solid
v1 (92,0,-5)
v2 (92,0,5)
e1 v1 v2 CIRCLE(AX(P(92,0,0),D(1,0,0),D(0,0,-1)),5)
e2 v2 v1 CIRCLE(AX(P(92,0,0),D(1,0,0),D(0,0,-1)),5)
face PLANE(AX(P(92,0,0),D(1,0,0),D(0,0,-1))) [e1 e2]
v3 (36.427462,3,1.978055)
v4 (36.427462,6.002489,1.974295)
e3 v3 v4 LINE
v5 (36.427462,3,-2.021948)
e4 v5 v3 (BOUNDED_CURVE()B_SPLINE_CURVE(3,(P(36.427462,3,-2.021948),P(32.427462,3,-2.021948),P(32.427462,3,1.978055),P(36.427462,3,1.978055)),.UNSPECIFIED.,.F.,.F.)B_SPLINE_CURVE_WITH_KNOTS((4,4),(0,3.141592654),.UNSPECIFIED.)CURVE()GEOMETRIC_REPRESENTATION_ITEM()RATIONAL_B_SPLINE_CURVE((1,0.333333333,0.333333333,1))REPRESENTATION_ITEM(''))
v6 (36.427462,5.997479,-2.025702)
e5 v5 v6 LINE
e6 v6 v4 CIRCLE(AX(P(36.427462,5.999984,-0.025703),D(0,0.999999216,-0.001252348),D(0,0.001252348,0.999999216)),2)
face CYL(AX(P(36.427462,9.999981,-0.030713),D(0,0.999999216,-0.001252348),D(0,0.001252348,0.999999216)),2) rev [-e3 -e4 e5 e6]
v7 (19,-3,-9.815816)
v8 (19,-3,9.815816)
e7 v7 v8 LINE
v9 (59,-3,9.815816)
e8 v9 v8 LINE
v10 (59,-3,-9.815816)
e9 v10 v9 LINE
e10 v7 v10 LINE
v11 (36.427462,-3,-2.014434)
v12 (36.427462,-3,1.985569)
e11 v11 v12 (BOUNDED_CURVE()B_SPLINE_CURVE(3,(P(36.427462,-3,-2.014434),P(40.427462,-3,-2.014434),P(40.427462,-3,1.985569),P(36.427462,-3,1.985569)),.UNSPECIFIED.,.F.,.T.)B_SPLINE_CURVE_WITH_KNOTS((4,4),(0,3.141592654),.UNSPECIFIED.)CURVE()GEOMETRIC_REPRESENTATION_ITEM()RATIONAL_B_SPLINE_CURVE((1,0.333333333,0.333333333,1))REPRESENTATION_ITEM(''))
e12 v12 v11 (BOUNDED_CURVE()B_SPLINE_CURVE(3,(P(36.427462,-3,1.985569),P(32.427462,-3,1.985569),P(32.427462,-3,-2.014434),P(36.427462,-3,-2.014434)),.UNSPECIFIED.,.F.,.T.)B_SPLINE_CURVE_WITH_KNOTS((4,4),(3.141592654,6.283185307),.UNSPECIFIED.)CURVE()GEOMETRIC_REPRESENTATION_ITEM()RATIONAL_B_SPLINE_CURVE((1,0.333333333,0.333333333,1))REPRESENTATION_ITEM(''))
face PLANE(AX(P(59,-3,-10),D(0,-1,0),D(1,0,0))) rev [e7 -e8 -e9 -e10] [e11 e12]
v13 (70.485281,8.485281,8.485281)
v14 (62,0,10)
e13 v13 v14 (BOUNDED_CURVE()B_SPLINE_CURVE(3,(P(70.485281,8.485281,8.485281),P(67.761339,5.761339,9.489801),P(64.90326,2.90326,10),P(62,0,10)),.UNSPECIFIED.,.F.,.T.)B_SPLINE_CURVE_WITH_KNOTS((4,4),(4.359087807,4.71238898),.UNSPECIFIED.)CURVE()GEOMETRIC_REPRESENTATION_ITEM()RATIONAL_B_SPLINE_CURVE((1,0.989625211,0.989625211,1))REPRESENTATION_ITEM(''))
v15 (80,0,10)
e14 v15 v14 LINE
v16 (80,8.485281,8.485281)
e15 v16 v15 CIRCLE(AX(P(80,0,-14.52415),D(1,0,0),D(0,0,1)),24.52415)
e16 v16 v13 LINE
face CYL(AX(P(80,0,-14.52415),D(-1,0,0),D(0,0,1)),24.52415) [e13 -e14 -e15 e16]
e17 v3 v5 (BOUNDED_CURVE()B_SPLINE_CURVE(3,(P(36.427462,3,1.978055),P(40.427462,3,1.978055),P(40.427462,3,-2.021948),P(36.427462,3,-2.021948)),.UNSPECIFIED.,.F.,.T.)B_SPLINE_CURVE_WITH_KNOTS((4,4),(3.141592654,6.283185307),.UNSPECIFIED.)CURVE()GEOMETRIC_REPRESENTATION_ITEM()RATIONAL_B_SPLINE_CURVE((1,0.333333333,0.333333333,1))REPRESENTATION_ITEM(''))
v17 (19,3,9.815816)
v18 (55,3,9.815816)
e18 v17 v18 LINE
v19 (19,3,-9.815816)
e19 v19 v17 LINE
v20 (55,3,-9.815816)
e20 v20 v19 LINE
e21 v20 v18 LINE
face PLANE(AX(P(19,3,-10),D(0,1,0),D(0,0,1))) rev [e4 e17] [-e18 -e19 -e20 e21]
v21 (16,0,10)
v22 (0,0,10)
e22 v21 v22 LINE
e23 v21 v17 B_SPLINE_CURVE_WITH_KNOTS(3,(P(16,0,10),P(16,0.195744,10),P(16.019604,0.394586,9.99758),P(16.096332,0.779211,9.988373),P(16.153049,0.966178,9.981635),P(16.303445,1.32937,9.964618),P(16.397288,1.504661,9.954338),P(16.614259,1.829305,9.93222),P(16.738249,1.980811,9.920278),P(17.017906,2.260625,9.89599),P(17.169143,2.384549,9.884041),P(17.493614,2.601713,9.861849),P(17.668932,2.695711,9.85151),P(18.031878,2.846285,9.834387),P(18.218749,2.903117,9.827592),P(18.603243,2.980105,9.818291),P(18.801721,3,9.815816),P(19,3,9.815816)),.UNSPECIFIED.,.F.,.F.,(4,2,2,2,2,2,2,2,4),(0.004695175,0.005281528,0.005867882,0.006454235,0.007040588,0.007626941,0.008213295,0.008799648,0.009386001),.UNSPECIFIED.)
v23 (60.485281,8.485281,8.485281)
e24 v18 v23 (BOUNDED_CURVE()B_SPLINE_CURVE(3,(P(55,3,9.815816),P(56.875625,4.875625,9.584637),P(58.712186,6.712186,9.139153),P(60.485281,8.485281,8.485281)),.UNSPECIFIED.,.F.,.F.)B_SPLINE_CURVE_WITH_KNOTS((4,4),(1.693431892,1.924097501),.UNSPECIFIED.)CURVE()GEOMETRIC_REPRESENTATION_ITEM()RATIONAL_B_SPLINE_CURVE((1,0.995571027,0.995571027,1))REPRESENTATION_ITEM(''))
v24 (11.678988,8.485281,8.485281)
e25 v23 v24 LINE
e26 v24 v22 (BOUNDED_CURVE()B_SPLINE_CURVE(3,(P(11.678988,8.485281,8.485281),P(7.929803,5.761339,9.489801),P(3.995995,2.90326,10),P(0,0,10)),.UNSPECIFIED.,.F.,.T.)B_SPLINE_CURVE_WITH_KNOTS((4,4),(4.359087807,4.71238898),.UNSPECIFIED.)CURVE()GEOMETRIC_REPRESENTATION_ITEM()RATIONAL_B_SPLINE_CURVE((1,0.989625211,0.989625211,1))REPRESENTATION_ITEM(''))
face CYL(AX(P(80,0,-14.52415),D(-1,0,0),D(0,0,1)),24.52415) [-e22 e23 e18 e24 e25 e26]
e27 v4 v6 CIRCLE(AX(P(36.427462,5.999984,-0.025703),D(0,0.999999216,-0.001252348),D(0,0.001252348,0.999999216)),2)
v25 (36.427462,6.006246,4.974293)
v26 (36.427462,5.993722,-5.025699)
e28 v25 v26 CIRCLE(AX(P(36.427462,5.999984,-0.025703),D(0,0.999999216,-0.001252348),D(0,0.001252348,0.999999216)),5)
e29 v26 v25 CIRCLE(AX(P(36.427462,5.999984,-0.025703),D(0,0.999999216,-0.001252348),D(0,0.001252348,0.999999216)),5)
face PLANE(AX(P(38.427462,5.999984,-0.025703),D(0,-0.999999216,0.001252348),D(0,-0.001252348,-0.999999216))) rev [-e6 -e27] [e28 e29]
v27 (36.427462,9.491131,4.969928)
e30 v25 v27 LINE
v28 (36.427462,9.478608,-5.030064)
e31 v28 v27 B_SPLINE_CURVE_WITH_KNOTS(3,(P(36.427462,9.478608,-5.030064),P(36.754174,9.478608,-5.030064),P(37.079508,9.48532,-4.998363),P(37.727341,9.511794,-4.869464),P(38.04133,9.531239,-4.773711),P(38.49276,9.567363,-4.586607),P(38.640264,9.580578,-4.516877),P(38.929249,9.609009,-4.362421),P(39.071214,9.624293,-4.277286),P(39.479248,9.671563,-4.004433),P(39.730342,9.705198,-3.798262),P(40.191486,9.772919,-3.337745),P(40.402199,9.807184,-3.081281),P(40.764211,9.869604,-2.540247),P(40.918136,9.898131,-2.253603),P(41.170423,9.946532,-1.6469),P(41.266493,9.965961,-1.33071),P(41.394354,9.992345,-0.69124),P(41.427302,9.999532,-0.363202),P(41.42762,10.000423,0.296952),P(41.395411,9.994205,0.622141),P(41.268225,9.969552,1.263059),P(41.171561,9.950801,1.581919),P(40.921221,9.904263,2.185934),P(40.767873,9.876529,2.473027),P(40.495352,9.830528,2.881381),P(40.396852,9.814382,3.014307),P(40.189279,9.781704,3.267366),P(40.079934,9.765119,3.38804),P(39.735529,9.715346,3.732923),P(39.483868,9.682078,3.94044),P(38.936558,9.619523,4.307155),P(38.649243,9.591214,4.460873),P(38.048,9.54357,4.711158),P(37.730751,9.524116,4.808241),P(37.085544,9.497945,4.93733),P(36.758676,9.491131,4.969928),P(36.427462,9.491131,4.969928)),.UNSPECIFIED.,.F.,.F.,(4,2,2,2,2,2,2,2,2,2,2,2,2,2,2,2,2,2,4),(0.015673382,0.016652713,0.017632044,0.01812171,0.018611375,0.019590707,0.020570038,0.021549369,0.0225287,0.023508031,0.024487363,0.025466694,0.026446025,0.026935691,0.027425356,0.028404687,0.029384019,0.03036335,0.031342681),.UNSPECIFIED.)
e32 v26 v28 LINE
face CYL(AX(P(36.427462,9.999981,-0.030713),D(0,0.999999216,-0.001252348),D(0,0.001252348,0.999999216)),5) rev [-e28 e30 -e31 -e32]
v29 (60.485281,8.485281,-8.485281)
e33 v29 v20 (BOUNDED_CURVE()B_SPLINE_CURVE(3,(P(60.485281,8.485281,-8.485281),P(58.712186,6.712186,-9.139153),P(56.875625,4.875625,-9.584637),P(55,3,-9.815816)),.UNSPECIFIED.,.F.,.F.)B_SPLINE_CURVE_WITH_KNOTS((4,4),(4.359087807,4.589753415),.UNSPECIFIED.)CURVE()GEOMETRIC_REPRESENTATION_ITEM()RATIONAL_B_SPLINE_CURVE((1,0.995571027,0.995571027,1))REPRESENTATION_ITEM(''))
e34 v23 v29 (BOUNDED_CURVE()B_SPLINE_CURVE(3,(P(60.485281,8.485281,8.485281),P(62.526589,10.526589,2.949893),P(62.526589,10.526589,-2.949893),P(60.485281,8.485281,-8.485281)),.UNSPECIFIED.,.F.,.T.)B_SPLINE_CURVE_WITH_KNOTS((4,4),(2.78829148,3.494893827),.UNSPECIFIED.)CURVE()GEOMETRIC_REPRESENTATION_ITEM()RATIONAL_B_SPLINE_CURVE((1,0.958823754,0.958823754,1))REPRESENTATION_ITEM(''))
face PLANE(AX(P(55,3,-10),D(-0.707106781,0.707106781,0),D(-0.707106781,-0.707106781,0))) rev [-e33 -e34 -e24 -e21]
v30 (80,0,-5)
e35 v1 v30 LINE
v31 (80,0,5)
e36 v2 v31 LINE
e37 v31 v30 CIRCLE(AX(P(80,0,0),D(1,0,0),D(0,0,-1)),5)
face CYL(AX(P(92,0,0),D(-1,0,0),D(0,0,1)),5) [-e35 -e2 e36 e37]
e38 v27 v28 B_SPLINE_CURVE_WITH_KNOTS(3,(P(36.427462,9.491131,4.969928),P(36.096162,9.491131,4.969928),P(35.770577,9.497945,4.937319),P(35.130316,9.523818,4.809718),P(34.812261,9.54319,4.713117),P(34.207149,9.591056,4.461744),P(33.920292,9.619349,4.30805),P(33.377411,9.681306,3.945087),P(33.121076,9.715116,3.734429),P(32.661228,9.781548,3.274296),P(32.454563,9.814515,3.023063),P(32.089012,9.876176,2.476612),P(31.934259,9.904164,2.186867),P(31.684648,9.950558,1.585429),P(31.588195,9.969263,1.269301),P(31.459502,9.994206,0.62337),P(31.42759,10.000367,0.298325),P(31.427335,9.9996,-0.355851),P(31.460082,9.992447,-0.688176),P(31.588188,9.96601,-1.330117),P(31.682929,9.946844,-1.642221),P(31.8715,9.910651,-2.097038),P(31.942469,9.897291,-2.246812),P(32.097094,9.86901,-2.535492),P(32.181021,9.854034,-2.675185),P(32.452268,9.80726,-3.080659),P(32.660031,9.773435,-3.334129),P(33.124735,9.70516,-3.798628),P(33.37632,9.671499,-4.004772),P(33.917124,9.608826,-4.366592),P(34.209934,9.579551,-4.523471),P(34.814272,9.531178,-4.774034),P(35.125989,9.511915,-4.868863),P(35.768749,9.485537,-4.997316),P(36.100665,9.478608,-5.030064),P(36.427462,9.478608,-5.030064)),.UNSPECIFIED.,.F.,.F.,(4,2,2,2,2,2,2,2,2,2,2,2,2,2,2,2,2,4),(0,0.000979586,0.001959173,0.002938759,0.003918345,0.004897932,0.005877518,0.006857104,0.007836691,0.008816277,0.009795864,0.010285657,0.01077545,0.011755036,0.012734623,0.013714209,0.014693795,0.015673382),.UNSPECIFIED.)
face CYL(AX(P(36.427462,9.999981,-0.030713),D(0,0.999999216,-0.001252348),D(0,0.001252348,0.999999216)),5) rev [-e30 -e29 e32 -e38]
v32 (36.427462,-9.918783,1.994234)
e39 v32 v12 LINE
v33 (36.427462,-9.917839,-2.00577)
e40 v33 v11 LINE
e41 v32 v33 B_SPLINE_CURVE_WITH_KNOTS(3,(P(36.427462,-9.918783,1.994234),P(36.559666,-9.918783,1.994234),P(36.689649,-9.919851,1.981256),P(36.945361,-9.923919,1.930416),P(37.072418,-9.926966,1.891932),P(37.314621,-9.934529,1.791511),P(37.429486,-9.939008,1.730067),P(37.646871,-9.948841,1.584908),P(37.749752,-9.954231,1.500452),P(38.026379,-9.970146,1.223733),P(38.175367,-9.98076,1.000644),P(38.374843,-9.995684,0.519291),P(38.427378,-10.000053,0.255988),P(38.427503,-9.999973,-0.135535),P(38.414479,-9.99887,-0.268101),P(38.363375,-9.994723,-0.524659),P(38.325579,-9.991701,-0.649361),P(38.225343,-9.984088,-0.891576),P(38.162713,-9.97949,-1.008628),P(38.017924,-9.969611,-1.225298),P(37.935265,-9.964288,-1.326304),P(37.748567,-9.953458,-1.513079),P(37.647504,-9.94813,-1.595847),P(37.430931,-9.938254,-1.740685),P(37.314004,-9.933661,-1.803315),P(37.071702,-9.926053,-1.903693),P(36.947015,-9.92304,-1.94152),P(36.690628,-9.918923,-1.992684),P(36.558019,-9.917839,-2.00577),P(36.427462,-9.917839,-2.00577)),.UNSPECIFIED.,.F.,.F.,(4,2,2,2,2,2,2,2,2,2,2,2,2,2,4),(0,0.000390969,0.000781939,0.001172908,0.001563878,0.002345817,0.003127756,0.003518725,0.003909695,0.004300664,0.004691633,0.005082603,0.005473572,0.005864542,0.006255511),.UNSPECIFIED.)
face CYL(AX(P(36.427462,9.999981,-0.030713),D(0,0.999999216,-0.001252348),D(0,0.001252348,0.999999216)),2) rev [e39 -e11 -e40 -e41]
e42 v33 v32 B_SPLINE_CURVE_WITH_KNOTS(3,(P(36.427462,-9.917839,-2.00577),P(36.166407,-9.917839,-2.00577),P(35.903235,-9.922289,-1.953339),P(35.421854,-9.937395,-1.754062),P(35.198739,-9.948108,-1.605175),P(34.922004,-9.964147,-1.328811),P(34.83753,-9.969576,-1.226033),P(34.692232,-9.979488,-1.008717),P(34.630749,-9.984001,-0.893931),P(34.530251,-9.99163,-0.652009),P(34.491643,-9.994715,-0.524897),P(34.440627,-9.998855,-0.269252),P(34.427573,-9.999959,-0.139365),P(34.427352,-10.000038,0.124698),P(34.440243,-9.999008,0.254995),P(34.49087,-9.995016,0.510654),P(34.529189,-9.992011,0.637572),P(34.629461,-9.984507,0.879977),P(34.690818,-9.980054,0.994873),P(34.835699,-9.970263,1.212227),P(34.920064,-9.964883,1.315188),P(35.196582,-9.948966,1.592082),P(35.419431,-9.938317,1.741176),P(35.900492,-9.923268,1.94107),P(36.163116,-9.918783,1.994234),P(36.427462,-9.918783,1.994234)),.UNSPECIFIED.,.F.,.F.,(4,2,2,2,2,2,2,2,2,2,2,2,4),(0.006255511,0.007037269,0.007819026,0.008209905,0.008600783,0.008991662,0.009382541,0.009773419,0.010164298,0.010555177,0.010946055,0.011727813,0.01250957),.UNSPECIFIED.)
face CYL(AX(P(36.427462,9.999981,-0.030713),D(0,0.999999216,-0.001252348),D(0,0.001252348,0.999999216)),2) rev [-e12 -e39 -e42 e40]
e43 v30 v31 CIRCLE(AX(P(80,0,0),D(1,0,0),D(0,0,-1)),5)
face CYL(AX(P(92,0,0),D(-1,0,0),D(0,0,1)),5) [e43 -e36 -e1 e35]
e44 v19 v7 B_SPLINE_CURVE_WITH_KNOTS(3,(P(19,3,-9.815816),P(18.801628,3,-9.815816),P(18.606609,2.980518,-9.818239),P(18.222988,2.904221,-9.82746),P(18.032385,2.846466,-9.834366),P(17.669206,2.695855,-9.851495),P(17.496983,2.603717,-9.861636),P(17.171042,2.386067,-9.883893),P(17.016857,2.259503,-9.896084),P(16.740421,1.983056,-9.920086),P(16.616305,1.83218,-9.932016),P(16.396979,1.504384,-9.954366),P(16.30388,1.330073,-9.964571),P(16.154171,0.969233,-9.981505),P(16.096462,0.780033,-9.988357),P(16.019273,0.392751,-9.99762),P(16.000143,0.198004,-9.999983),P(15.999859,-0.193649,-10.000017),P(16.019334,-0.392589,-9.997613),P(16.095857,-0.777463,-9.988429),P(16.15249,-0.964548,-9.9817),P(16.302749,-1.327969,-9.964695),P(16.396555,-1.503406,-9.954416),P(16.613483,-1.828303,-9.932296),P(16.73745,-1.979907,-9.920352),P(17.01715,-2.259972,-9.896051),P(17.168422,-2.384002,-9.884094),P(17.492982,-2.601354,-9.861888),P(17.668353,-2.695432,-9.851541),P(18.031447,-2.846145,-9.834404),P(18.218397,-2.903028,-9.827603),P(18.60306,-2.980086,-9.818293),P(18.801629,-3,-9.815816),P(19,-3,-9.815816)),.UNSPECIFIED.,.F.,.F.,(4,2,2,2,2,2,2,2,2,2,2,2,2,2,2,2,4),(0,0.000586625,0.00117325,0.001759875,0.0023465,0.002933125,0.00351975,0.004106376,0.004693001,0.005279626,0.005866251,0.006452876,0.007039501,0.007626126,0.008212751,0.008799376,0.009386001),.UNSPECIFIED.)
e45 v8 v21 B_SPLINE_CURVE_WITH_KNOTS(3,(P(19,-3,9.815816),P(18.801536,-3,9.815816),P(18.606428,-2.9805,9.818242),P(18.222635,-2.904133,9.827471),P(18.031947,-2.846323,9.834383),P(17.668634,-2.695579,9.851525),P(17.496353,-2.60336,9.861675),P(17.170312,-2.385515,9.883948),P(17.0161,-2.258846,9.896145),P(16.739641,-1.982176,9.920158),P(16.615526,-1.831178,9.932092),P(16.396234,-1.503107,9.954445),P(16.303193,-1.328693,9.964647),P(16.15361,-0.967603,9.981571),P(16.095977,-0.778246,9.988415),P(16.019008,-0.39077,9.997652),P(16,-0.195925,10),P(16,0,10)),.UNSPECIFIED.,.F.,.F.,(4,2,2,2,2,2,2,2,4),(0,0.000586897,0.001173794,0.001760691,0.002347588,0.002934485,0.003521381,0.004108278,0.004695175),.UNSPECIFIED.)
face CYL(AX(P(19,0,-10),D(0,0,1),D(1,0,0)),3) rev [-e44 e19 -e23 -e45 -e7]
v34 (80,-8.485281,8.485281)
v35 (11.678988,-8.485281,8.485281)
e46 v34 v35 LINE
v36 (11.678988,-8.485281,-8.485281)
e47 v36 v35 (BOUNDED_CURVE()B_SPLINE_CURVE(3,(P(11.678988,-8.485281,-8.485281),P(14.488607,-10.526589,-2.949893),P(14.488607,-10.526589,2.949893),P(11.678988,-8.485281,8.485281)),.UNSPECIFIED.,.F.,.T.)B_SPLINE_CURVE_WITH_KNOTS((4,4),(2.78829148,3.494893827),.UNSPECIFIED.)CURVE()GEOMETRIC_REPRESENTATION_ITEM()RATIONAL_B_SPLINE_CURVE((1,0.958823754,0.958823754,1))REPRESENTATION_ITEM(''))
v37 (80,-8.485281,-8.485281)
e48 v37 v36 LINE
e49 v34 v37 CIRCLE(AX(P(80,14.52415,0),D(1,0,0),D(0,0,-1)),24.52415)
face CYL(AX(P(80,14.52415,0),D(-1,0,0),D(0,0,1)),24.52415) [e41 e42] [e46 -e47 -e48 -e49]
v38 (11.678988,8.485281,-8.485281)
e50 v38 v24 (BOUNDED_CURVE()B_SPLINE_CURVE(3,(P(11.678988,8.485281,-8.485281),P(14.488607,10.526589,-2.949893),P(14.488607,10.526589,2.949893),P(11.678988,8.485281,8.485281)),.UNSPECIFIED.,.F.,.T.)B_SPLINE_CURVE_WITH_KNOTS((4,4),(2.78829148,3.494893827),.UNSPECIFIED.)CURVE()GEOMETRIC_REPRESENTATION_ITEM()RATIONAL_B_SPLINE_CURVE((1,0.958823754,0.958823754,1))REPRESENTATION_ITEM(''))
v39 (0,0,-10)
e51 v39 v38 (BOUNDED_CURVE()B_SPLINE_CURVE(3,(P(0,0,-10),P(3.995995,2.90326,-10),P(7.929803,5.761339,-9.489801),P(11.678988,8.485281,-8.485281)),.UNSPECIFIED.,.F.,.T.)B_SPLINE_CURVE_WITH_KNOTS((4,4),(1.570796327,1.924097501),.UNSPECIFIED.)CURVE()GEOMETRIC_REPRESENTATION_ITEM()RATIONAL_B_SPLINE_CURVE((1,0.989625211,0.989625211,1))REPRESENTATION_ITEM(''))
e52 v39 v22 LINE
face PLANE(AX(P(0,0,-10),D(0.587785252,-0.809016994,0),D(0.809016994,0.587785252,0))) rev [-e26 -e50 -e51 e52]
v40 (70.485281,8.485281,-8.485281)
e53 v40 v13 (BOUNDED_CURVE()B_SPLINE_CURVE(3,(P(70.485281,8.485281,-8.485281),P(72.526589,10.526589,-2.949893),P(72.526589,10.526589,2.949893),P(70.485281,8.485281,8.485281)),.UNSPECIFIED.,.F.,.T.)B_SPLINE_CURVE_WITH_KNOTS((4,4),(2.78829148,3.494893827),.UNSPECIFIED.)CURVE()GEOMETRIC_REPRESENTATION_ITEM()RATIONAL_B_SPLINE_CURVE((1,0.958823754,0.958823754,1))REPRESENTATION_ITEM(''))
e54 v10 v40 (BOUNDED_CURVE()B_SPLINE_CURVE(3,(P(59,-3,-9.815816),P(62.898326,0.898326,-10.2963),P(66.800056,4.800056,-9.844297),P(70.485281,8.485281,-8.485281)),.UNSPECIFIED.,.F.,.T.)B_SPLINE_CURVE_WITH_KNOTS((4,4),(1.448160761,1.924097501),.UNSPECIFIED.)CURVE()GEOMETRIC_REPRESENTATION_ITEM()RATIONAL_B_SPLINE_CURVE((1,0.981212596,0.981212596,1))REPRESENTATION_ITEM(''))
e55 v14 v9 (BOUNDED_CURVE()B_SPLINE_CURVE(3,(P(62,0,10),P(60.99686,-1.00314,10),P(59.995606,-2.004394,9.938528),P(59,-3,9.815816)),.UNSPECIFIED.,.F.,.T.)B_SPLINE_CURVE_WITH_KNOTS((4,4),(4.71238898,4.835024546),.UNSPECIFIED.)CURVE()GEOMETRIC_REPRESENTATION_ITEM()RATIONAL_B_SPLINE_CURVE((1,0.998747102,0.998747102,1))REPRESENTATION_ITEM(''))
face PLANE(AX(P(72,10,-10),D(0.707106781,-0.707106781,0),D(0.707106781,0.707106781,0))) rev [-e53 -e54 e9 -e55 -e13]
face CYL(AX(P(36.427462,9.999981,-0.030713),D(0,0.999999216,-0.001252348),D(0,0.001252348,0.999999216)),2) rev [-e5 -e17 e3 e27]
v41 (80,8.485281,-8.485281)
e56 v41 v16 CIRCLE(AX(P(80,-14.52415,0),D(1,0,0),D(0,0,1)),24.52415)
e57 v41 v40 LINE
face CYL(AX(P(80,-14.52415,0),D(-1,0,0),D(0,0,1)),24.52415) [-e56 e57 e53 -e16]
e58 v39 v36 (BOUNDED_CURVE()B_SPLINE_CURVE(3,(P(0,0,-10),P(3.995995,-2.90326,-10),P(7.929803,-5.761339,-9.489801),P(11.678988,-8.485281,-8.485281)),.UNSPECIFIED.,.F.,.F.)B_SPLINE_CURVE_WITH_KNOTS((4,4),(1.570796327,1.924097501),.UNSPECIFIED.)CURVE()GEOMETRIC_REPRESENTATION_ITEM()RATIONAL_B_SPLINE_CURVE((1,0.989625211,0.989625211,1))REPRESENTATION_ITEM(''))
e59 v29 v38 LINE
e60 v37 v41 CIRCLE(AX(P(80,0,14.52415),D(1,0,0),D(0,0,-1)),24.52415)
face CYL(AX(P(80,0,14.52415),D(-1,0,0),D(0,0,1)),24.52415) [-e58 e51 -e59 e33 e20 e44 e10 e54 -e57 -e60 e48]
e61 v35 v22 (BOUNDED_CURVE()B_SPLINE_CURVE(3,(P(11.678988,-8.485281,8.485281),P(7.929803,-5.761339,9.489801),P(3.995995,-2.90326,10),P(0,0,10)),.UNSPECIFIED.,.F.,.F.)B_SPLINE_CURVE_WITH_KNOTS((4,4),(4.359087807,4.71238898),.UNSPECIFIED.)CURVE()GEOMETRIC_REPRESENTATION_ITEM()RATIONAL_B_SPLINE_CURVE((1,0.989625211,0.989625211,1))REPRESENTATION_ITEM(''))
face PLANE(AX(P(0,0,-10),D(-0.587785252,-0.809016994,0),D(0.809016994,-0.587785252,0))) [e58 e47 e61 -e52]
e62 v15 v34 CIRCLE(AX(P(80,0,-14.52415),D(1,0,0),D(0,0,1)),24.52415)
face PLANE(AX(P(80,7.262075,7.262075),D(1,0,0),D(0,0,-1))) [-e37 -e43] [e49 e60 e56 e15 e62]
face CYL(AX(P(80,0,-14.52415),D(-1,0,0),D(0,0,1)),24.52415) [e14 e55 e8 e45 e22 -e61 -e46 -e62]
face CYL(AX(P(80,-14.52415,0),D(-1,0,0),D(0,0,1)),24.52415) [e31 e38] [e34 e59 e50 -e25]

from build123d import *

# Parameters (mm, degrees)
PIN_BODY_80MM_DEPTH             = 80
ARROW_NOSE_CUT_DEPTH            = 82.240384046
ARROW_NOSE_CUT_DEPTH_BACK       = 82.240384046
SLOT_AND_STEP_CUT_DEPTH         = 82.240384046
SLOT_AND_STEP_CUT_DEPTH_BACK    = 82.240384046
SPIGOT_PROFILE_10_R             = 5
SPIGOT_10X12_DEPTH              = 12
COUNTERBORED_HOLE_4_D           = 4
COUNTERBORED_HOLE_4_DEPTH       = 100
COUNTERBORED_HOLE_4_CBORE_D     = 10
COUNTERBORED_HOLE_4_CBORE_DEPTH = 4


with BuildPart() as part:
    # Pin Body Profile → Pin Body 80mm (new body)
    with BuildSketch(Plane(origin=(0, 0, 0), x_dir=(0, 0, -1), z_dir=(1, 0, 0))):
        with BuildLine():
            ThreePointArc((-8.485281374, -8.485281374), (-10, 0), (-8.485281374, 8.485281374))
            ThreePointArc((-8.485281374, 8.485281374), (0, 10), (8.485281374, 8.485281374))
            ThreePointArc((8.485281374, 8.485281374), (10, 0), (8.485281374, -8.485281374))
            ThreePointArc((8.485281374, -8.485281374), (0, -10), (-8.485281374, -8.485281374))
        make_face()
    extrude(amount=PIN_BODY_80MM_DEPTH)

    # Arrow Nose Profile 72deg → Arrow Nose Cut (cut, two sides: drawn at the far end of the back side and taken through both)
    with BuildSketch(Plane.XY.offset(-ARROW_NOSE_CUT_DEPTH_BACK)):
        Polygon((0, 10), (0, 0), (13.763819205, 10), align=None)
        Polygon((13.763819205, -10), (0, 0), (0, -10), align=None)
    extrude(amount=ARROW_NOSE_CUT_DEPTH + ARROW_NOSE_CUT_DEPTH_BACK, mode=Mode.SUBTRACT)

    # Slot and Step Profile → Slot and Step Cut (cut, two sides: drawn at the far end of the back side and taken through both)
    with BuildSketch(Plane.XY.offset(-SLOT_AND_STEP_CUT_DEPTH_BACK)):
        with BuildLine():
            Line((72, 10), (59, -3))
            Line((59, -3), (19, -3))
            ThreePointArc((19, -3), (16, 0), (19, 3))
            Line((19, 3), (55, 3))
            Line((55, 3), (62, 10))
            Line((62, 10), (72, 10))
        make_face()
    extrude(amount=SLOT_AND_STEP_CUT_DEPTH + SLOT_AND_STEP_CUT_DEPTH_BACK, mode=Mode.SUBTRACT)

    # Spigot Profile Ø10 → Spigot Ø10x12 (add)
    with BuildSketch(Plane(origin=(80, 0, 0), x_dir=(0, 0, -1), z_dir=(1, 0, 0))):
        Circle(SPIGOT_PROFILE_10_R)
    extrude(amount=SPIGOT_10X12_DEPTH)

    # Counterbored Hole Ø4
    with Locations(Plane(origin=(36.427461815, 9.999980768, -0.030712762), x_dir=(0, 0.001252347692, 0.999999215812), z_dir=(0, 0.999999215812, -0.001252347692))):
        with Locations((0, 0)):
            CounterBoreHole(COUNTERBORED_HOLE_4_D / 2, COUNTERBORED_HOLE_4_CBORE_D / 2, COUNTERBORED_HOLE_4_CBORE_DEPTH, depth=COUNTERBORED_HOLE_4_DEPTH)


solid = part.part
